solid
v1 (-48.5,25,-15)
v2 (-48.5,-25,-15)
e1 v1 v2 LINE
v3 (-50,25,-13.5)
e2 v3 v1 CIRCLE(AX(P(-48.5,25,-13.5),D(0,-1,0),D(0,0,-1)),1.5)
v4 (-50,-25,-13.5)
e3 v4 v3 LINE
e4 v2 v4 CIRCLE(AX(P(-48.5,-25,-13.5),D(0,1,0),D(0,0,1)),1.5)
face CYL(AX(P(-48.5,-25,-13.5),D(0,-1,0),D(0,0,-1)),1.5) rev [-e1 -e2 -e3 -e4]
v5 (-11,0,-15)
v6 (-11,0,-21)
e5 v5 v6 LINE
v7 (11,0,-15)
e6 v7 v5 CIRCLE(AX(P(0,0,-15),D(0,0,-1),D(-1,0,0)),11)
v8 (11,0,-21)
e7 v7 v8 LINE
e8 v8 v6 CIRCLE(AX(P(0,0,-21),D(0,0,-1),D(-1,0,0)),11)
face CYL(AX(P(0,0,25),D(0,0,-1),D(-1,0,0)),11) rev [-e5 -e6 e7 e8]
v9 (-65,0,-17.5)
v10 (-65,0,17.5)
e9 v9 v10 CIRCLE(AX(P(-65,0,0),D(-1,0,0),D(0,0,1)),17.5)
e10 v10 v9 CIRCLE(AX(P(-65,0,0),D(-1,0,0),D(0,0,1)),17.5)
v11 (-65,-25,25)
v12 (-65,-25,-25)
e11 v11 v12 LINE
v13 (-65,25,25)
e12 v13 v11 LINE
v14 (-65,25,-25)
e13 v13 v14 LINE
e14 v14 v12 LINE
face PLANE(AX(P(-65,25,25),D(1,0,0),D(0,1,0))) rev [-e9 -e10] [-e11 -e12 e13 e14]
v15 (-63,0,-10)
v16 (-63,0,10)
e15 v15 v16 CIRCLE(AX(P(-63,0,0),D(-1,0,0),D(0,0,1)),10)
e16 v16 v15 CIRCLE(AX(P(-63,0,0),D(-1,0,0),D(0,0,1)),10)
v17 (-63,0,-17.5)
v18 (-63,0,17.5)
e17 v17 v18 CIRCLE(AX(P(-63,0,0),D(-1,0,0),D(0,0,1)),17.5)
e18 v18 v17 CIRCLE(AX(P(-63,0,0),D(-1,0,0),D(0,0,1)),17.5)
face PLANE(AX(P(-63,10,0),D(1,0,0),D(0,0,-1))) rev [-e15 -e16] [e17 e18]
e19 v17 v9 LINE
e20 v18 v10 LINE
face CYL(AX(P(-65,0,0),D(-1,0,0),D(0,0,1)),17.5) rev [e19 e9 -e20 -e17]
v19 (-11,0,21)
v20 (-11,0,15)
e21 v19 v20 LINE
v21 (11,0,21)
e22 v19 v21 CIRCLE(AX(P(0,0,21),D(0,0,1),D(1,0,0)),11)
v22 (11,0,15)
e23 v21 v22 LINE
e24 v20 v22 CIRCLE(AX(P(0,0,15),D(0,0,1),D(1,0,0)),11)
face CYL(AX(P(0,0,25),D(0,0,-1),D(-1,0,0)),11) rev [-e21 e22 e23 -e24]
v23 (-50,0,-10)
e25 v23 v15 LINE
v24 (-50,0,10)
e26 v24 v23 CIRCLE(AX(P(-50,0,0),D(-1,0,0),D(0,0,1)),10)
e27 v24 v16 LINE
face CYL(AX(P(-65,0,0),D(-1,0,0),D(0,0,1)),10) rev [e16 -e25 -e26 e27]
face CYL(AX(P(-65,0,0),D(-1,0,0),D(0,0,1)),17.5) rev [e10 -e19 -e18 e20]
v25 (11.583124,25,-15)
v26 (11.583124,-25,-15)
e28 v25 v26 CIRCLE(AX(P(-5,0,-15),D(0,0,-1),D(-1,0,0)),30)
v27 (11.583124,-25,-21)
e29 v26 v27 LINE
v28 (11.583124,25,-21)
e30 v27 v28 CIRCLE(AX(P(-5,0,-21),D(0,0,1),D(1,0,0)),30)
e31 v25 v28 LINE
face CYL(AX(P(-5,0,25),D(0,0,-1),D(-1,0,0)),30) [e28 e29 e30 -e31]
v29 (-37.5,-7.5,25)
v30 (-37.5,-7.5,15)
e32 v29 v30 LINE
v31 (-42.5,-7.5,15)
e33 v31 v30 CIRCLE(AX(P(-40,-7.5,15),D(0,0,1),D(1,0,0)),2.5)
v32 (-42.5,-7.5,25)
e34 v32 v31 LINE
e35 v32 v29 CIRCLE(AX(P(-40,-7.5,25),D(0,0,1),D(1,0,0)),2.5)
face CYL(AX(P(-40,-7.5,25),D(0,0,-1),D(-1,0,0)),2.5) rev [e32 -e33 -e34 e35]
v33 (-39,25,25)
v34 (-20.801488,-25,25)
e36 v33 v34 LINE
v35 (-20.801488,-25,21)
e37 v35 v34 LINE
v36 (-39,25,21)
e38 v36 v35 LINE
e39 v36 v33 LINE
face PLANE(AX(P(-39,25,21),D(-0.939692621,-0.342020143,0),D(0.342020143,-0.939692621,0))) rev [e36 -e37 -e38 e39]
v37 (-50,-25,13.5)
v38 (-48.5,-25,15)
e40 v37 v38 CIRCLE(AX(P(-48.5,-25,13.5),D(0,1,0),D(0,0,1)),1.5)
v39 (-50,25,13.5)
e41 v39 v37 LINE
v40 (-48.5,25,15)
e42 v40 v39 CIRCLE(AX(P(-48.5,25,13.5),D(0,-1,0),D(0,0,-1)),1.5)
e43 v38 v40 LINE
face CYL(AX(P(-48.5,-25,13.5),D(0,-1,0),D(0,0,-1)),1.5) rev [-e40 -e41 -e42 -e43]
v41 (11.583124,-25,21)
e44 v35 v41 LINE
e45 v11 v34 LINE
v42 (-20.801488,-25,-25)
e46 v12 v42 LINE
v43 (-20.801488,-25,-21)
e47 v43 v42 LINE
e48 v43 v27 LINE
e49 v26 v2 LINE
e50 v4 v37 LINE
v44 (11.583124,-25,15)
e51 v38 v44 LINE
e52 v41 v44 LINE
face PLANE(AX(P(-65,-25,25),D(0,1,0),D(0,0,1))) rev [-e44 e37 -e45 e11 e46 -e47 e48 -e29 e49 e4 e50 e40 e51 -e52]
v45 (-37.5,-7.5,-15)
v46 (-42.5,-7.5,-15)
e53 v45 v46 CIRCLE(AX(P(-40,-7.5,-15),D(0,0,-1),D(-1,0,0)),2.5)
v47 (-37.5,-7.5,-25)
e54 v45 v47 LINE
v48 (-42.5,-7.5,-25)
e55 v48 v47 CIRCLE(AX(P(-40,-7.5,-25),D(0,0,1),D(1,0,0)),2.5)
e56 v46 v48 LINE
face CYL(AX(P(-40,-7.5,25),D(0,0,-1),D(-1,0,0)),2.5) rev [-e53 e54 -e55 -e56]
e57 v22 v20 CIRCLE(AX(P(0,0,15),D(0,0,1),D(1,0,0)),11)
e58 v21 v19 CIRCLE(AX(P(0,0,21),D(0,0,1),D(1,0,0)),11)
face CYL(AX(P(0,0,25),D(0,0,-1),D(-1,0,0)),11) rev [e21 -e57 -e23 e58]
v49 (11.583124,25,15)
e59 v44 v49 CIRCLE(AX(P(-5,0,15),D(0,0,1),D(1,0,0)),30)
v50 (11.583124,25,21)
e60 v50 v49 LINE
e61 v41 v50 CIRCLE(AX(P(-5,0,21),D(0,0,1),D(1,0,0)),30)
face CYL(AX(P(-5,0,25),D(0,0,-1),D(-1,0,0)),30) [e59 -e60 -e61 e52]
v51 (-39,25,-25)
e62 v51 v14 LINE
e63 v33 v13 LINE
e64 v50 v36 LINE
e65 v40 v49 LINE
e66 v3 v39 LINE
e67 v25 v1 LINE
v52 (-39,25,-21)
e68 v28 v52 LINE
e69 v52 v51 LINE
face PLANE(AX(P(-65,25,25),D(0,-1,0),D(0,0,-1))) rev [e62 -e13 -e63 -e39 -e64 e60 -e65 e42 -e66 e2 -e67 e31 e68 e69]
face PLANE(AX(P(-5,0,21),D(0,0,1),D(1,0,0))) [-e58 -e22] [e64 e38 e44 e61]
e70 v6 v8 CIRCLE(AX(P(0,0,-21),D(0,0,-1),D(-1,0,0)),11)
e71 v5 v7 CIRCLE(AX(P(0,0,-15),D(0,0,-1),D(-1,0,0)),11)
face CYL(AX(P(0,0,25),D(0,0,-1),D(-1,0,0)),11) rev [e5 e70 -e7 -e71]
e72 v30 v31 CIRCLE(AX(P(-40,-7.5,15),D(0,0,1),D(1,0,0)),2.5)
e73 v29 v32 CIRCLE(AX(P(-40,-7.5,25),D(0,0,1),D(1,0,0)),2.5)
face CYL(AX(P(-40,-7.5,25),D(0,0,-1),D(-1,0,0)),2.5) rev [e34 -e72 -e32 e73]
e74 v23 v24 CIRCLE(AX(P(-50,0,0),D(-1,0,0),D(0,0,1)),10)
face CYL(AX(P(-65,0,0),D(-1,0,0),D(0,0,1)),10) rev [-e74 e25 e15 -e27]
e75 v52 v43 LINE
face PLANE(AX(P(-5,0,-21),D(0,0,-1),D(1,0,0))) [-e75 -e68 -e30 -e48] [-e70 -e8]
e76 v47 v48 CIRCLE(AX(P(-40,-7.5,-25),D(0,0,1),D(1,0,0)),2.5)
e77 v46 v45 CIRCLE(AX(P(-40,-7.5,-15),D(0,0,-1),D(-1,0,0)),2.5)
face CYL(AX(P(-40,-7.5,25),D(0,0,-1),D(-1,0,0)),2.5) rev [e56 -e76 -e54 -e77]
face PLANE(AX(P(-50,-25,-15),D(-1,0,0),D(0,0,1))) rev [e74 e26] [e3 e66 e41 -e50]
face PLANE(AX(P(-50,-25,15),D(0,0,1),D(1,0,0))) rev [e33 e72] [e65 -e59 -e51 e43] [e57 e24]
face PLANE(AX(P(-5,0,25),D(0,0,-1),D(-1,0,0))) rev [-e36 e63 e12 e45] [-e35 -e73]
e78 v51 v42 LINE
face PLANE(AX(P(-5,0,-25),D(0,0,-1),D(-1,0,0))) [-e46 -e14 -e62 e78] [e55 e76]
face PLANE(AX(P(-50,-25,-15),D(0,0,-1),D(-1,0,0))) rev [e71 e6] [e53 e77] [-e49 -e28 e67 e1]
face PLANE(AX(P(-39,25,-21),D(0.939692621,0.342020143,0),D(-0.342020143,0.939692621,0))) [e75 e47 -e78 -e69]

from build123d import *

# Parameters (mm, degrees)
CLEVIS_BODY_PROFILE_R   = 11
CLEVIS_BODY_PROFILE_R_2 = 2.5
CLEVIS_BODY_DEPTH       = 25
CLEVIS_SLOT_SKETCH_W    = 90.532278548
CLEVIS_SLOT_SKETCH_H    = 30
CLEVIS_SLOT_30MM_DEPTH  = 86.732140997
EAR_SIDE_RELIEF_DEPTH   = 4
SLOT_FILLET_R1_5_R      = 1.5


with BuildPart() as part:
    # Clevis Body Profile → Clevis Body (new, symmetric)
    with BuildSketch(Plane.XY):
        with BuildLine():
            Line((-65, 25), (11.583123952, 25))
            ThreePointArc((11.583123952, 25), (25, 0), (11.583123952, -25))
            Line((11.583123952, -25), (-65, -25))
            Line((-65, -25), (-65, 25))
        make_face()
        Circle(CLEVIS_BODY_PROFILE_R, mode=Mode.SUBTRACT)
        with Locations((-40, -7.5)):
            Circle(CLEVIS_BODY_PROFILE_R_2, mode=Mode.SUBTRACT)
    extrude(amount=CLEVIS_BODY_DEPTH, both=True)

    # Clevis Slot Sketch → Clevis Slot 30mm (cut, through all)
    with BuildSketch(Plane(origin=(0, 25, 0), x_dir=(1, 0, 0), z_dir=(0, 1, 0))):
        with Locations((-4.733860726, 0)):
            Rectangle(CLEVIS_SLOT_SKETCH_W, CLEVIS_SLOT_SKETCH_H)
    extrude(amount=-CLEVIS_SLOT_30MM_DEPTH, mode=Mode.SUBTRACT)

    # Ear Side Relief Sketch → Ear Side Relief (cut)
    with BuildSketch(Plane.XY.offset(25)):
        with BuildLine():
            Line((-39, 25), (-20.801488287, -25))
            Line((-20.801488287, -25), (11.583123952, -25))
            ThreePointArc((11.583123952, -25), (25, 0), (11.583123952, 25))
            Line((11.583123952, 25), (-39, 25))
        make_face()
    ear_side_relief = extrude(amount=-EAR_SIDE_RELIEF_DEPTH, mode=Mode.SUBTRACT)

    # Ear Side Relief Mirror: Ear Side Relief across plane
    add(ear_side_relief.mirror(Plane.XY), mode=Mode.SUBTRACT)

    # Slot Fillet R1.5
    slot_fillet_r1_5_edges = [part.edges().sort_by_distance(p)[0] for p in [
        (-50, 0, -15),
        (-50, 0, 15),
    ]]
    fillet(slot_fillet_r1_5_edges, radius=SLOT_FILLET_R1_5_R)

    # Sketch4 → Pin Bore Ø20 CBore Ø35 (revolve, cut)
    with BuildSketch(Plane(origin=(-65, 0, 0), x_dir=(0, 0, 1), z_dir=(0, 1, 0))):
        Polygon((0, 0), (0, 99.718353376), (10, 99.718353376), (10, 2), (17.5, 2), (17.5, 0), align=None)
    revolve(axis=Axis((45, 0, 0), (-1, 0, 0)), mode=Mode.SUBTRACT)


solid = part.part
